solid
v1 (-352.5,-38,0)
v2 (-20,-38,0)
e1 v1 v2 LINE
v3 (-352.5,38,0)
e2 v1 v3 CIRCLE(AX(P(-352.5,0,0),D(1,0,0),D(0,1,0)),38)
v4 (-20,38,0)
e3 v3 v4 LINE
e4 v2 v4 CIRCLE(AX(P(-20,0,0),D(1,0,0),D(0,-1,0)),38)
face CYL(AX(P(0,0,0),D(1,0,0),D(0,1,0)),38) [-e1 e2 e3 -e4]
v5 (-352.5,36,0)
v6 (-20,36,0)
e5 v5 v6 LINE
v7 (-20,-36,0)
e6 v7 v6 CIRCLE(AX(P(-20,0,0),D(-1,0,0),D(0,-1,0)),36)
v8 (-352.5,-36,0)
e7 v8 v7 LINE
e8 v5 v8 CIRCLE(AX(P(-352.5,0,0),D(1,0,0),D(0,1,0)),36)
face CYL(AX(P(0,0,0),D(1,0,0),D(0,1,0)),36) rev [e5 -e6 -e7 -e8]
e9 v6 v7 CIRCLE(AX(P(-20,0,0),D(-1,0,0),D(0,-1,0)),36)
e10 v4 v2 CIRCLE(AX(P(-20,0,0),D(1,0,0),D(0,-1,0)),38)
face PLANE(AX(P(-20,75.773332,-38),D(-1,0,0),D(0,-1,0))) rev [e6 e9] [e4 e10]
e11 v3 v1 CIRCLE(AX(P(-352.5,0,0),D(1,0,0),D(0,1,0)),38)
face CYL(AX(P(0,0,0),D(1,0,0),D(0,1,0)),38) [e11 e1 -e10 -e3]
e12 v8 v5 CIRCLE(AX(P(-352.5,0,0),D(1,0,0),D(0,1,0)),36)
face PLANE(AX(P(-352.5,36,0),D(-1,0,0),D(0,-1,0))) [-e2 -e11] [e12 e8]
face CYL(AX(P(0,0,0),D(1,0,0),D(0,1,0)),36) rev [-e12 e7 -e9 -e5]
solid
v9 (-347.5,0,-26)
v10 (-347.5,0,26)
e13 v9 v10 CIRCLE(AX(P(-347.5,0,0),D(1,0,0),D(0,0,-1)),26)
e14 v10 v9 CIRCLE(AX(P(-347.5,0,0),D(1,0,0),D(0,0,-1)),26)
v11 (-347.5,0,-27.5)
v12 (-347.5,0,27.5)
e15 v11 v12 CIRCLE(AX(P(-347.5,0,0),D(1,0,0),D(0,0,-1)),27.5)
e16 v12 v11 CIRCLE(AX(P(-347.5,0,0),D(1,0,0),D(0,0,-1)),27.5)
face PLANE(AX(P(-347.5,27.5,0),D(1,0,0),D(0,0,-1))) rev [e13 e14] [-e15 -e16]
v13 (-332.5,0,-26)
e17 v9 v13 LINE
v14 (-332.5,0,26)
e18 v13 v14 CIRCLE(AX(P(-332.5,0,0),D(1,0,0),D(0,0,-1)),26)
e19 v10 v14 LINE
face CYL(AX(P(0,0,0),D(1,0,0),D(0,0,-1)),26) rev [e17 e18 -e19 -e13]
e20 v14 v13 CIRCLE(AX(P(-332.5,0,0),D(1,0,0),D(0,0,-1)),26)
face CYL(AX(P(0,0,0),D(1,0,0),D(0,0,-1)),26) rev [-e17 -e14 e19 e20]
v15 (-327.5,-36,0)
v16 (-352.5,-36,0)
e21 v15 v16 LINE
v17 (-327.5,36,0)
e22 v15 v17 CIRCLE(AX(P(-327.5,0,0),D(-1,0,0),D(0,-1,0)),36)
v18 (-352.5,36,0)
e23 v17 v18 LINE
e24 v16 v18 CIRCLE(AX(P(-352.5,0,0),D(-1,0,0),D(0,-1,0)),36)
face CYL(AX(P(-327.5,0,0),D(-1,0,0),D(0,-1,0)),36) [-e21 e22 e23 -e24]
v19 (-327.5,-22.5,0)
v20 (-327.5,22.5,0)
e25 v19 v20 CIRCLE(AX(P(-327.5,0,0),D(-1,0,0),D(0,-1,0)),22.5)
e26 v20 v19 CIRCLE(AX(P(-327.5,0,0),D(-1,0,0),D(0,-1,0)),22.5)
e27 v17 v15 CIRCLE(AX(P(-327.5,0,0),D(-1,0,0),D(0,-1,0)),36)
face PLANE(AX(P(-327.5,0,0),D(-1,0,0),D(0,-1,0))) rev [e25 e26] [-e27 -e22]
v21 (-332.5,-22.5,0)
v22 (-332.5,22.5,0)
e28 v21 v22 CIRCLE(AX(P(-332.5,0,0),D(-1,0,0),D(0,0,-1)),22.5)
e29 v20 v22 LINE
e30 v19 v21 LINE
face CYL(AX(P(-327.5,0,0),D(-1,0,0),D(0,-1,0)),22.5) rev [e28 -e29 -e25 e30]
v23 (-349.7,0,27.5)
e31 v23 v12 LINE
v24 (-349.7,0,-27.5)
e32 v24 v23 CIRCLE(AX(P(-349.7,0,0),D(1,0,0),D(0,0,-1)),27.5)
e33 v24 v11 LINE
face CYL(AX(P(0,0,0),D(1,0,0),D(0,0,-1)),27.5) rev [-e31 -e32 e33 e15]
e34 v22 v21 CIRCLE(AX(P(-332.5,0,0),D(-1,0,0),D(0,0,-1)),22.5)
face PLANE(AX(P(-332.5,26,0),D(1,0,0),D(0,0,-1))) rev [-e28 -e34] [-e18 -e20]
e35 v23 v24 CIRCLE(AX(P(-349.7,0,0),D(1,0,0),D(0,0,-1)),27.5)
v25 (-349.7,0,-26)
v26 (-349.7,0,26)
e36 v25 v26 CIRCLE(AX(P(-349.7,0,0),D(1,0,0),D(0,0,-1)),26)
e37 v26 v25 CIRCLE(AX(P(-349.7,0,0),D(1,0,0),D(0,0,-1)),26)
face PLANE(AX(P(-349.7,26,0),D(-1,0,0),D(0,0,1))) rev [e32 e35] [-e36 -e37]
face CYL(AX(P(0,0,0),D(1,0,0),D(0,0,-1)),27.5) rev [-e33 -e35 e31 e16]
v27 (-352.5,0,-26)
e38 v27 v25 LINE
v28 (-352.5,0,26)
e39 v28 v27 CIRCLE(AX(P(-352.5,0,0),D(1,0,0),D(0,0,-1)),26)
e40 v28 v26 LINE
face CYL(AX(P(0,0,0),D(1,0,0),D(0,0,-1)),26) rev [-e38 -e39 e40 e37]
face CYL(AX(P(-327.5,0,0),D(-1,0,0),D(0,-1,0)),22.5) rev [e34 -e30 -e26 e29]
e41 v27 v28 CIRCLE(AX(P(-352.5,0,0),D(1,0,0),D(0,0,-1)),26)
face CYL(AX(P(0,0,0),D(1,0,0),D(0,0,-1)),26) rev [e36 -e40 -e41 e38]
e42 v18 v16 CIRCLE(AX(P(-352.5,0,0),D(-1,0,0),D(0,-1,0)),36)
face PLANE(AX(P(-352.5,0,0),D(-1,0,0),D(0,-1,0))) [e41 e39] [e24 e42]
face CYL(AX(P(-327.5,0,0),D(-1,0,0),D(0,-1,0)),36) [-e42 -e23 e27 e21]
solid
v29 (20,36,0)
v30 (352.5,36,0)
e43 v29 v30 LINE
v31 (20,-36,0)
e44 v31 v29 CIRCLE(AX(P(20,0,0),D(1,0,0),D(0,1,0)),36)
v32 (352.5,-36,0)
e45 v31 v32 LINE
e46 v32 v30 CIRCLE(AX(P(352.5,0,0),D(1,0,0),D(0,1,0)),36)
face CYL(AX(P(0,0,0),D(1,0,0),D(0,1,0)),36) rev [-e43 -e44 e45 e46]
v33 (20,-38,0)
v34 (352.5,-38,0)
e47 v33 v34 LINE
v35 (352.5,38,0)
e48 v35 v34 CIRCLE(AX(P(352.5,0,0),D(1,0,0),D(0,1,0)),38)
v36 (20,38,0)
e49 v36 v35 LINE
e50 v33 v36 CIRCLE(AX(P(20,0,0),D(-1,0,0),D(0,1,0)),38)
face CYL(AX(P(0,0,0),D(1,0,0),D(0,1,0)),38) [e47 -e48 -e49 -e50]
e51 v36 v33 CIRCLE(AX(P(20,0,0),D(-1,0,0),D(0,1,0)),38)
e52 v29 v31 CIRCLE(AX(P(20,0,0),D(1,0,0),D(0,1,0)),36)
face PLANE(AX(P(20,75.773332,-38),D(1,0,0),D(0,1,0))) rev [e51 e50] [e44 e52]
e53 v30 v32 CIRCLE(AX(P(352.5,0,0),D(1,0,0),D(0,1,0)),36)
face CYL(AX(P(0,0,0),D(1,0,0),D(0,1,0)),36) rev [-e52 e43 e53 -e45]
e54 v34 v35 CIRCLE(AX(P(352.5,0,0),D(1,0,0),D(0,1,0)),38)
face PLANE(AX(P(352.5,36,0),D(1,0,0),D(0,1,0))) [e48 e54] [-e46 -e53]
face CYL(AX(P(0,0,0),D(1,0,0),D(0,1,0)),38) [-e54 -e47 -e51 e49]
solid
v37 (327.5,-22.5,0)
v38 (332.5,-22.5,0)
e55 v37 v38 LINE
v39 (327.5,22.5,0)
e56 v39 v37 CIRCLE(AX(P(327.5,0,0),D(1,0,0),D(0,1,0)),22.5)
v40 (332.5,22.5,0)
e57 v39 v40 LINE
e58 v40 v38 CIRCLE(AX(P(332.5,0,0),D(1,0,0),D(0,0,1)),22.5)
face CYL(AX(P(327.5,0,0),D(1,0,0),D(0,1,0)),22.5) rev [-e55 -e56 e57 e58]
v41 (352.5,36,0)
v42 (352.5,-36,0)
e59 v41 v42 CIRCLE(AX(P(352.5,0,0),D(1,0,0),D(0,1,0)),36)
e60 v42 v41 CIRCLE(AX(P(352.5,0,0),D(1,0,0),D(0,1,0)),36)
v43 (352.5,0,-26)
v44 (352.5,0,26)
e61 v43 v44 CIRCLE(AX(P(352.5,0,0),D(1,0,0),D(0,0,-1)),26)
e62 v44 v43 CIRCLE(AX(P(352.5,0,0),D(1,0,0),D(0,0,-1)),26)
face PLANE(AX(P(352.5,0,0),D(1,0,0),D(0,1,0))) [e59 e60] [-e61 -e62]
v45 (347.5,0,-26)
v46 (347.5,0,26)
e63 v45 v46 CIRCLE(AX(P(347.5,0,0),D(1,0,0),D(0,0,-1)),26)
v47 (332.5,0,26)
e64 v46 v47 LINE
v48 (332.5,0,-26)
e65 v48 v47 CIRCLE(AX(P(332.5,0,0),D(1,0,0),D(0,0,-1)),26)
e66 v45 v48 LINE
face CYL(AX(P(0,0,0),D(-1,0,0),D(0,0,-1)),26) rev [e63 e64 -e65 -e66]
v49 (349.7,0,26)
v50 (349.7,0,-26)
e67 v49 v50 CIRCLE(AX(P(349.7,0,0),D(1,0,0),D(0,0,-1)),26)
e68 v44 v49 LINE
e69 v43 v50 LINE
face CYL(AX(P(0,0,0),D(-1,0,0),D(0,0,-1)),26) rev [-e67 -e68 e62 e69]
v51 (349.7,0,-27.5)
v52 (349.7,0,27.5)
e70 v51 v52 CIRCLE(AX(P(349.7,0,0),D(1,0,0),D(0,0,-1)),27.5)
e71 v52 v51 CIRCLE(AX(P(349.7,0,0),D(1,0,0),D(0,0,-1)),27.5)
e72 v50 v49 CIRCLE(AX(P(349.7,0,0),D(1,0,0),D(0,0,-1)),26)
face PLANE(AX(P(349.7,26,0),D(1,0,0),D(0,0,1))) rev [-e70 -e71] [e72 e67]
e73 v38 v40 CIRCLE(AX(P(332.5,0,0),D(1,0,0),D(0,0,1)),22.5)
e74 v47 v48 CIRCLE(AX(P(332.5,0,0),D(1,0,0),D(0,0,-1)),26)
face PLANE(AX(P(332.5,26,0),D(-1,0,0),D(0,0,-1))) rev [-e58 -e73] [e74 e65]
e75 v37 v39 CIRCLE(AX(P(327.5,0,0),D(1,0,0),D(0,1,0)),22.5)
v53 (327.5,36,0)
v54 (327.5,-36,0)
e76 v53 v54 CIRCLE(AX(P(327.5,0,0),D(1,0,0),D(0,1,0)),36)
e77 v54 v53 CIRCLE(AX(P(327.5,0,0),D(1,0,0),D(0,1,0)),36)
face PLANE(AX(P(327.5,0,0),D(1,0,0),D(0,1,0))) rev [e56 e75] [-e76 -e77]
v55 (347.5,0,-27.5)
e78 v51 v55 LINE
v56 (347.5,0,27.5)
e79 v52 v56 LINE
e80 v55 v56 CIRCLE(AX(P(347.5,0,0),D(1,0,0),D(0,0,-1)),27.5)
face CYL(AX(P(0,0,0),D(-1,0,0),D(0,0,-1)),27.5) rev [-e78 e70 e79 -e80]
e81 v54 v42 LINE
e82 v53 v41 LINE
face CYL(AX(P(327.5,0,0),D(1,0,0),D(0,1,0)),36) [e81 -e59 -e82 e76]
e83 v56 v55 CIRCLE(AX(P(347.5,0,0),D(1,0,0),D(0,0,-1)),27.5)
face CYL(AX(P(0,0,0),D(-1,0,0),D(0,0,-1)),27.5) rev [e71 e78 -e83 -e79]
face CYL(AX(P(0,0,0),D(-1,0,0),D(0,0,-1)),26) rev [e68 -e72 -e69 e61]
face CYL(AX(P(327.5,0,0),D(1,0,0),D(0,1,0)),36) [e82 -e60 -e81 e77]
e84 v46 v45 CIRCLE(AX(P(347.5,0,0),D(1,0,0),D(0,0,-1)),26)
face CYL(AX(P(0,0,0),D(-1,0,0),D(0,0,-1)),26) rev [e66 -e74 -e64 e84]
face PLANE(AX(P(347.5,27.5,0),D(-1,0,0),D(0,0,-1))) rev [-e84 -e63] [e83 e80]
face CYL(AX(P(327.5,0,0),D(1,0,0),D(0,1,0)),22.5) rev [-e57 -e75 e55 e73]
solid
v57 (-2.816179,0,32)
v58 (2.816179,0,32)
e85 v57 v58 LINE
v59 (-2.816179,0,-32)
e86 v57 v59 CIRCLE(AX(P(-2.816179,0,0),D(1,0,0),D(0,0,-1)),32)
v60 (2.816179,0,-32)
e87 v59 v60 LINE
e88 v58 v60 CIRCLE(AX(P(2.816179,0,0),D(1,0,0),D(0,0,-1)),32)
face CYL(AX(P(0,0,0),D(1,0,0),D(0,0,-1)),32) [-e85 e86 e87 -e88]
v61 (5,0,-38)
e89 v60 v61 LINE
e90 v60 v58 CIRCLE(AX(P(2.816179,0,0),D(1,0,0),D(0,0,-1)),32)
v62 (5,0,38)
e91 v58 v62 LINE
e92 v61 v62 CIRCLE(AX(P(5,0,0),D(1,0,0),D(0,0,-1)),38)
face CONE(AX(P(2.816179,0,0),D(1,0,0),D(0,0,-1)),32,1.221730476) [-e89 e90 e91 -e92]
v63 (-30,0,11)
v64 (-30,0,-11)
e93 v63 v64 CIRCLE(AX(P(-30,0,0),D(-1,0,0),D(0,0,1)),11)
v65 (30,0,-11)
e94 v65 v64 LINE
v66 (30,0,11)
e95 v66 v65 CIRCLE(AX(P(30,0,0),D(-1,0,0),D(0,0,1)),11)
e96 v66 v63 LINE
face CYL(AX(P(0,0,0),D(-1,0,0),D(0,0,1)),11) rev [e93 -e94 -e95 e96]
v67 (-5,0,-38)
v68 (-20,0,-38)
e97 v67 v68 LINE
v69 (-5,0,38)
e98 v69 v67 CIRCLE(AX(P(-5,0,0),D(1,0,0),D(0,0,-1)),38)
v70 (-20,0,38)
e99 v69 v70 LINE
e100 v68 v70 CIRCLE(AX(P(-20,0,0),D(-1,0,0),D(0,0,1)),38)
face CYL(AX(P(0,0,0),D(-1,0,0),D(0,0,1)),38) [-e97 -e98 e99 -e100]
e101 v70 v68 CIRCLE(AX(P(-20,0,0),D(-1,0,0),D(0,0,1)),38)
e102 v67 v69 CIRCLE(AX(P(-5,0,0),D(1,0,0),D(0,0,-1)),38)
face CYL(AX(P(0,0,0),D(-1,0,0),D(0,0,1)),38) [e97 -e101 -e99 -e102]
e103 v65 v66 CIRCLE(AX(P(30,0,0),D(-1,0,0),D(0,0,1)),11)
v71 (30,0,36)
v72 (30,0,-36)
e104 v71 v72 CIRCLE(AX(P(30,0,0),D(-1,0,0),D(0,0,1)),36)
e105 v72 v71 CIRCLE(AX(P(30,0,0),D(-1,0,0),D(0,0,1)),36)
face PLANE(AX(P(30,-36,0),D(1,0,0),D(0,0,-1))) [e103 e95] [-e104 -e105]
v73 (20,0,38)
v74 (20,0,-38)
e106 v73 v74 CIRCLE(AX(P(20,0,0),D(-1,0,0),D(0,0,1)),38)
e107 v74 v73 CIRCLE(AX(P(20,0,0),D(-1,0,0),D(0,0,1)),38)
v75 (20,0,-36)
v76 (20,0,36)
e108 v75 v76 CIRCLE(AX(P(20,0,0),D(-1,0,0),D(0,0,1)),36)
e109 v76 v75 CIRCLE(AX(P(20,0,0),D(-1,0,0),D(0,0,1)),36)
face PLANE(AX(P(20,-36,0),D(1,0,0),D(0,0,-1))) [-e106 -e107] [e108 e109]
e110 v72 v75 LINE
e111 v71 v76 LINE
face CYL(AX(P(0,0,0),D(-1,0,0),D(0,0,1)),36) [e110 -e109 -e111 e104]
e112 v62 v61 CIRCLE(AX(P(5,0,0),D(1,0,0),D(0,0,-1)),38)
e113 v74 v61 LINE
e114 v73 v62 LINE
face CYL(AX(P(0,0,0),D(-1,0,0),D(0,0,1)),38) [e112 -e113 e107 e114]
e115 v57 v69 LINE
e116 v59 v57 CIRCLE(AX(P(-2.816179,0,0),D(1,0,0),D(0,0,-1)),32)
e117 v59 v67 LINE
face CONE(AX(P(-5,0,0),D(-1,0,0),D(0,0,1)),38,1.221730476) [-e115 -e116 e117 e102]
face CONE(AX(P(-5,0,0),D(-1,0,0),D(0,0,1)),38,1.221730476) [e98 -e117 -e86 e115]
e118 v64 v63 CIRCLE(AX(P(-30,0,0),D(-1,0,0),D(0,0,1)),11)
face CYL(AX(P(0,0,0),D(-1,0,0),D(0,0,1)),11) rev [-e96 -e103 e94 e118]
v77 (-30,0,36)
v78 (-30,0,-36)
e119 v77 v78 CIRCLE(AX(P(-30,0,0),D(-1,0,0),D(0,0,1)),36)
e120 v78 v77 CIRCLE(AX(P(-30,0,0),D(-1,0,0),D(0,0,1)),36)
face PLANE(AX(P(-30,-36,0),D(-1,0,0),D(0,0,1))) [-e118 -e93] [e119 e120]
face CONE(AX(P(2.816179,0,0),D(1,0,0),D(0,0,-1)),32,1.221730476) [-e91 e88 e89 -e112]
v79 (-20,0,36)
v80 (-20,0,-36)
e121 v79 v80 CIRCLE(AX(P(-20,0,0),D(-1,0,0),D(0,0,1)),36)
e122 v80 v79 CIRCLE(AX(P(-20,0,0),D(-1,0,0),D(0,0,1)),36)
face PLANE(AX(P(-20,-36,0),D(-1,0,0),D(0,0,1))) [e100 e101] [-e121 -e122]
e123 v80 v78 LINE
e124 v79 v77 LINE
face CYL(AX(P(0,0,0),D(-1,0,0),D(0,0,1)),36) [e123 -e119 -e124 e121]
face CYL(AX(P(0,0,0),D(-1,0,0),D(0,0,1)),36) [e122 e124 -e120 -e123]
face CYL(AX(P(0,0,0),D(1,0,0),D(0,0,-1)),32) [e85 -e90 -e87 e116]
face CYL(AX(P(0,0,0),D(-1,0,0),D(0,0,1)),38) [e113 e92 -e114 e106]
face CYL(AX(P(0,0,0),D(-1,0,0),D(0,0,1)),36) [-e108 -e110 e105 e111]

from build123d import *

# Parameters (mm, degrees)
SKETCH_1_W               = 705
SKETCH_1_H               = 2
SKETCH_2_R               = 36
SKETCH_2_R_2             = 22.5
EXTRUDE_1_DEPTH          = 25
SKETCH_3_R               = 36
SKETCH_3_R_2             = 22.5
EXTRUDE_2_DEPTH          = 25
CUT_EXTRUDE_1_DEPTH      = 357.572923818
CUT_EXTRUDE_1_DEPTH_BACK = 357.572923818
SKETCH_8_W               = 40
SKETCH_8_H               = 151.546664998


with BuildPart() as part:
    # 草图1 → 旋转1 (revolve)
    with BuildSketch(Plane.XY):
        with Locations((0, 37)):
            Rectangle(SKETCH_1_W, SKETCH_1_H)
    revolve(axis=Axis((0, 0, 0), (-1, 0, 0)))

    # 草图8 → 切除-拉伸1 (cut, two sides: drawn at the far end of the back side and taken through both)
    with BuildSketch(Plane.XY.offset(-CUT_EXTRUDE_1_DEPTH_BACK)):
        Rectangle(SKETCH_8_W, SKETCH_8_H)
    extrude(amount=CUT_EXTRUDE_1_DEPTH + CUT_EXTRUDE_1_DEPTH_BACK, mode=Mode.SUBTRACT)


with BuildPart() as body_2:
    # 草图2 → 凸台-拉伸1 (new body)
    with BuildSketch(Plane.ZY.offset(352.5)):
        with Locations(Location((0, 0, 0), (0, 0, 270))):
            Circle(SKETCH_2_R)
        with Locations(Location((0, 0, 0), (0, 0, 270))):
            Circle(SKETCH_2_R_2, mode=Mode.SUBTRACT)
    extrude(amount=-EXTRUDE_1_DEPTH)

    # 草图5 → 切除-旋转6 (revolve, cut)
    with BuildSketch(Plane.XY, mode=Mode.PRIVATE) as cut_revolve_6_sk:
        Polygon((-352.5, 26), (-349.7, 26), (-349.7, 27.5), (-347.5, 27.5), (-347.5, 26), (-332.5, 26), (-332.5, 0), (-352.5, 0), align=None)
    cut_revolve_6 = revolve(cut_revolve_6_sk.sketch.rotate(Axis((0, 0, 0), (-1, 0, 0)), 90), axis=Axis((0, 0, 0), (-1, 0, 0)), mode=Mode.SUBTRACT)


with BuildPart() as body_3:
    # 草图3 → 凸台-拉伸2 (new body)
    with BuildSketch(Plane(origin=(352.5, 0, 0), x_dir=(0, 0, -1), z_dir=(1, 0, 0))):
        with Locations(Location((0, 0, 0), (0, 0, 90))):
            Circle(SKETCH_3_R)
        with Locations(Location((0, 0, 0), (0, 0, 90))):
            Circle(SKETCH_3_R_2, mode=Mode.SUBTRACT)
    extrude(amount=-EXTRUDE_2_DEPTH)

    # 镜向2: 切除-旋转6 across plane
    add(cut_revolve_6.mirror(Plane(origin=(0, 0, 0), x_dir=(0, 0, 1), z_dir=(1, 0, 0))), mode=Mode.SUBTRACT)


with BuildPart() as cut_extrude_1_piece_1:
    # of the separate pieces the step leaves, piece 1, a body of its own (cut_extrude_1_pieces)
    add(part.part.solids().sort_by_distance((352.5, 36, 0))[0])


with BuildPart() as cut_extrude_1_piece_2:
    # of the separate pieces the step leaves, piece 2, a body of its own (cut_extrude_1_pieces)
    add(part.part.solids().sort_by_distance((-352.5, 36, 0))[0])


with BuildPart() as body_5:
    # 草图7 → 旋转2 (revolve)
    with BuildSketch(Plane.XY, mode=Mode.PRIVATE) as revolve_2_sk:
        Polygon((-30, -36), (-20, -36), (-20, -38), (20, -38), (20, -36), (30, -36), (30, -11), (-30, -11), align=None)
    revolve(revolve_2_sk.sketch.rotate(Axis((0, 0, 0), (1, 0, 0)), 270), axis=Axis((0, 0, 0), (1, 0, 0)))

    # 草图6 → 切除-旋转7 (revolve, cut)
    with BuildSketch(Plane.XY, mode=Mode.PRIVATE) as cut_revolve_7_sk:
        Polygon((-2.816178594, 32), (2.816178594, 32), (5, 38), (-5, 38), align=None)
    revolve(cut_revolve_7_sk.sketch.rotate(Axis((0, 0, 0), (-1, 0, 0)), 90), axis=Axis((0, 0, 0), (-1, 0, 0)), mode=Mode.SUBTRACT)


solid = Compound([body_2.part, body_3.part, cut_extrude_1_piece_1.part, cut_extrude_1_piece_2.part, body_5.part])
